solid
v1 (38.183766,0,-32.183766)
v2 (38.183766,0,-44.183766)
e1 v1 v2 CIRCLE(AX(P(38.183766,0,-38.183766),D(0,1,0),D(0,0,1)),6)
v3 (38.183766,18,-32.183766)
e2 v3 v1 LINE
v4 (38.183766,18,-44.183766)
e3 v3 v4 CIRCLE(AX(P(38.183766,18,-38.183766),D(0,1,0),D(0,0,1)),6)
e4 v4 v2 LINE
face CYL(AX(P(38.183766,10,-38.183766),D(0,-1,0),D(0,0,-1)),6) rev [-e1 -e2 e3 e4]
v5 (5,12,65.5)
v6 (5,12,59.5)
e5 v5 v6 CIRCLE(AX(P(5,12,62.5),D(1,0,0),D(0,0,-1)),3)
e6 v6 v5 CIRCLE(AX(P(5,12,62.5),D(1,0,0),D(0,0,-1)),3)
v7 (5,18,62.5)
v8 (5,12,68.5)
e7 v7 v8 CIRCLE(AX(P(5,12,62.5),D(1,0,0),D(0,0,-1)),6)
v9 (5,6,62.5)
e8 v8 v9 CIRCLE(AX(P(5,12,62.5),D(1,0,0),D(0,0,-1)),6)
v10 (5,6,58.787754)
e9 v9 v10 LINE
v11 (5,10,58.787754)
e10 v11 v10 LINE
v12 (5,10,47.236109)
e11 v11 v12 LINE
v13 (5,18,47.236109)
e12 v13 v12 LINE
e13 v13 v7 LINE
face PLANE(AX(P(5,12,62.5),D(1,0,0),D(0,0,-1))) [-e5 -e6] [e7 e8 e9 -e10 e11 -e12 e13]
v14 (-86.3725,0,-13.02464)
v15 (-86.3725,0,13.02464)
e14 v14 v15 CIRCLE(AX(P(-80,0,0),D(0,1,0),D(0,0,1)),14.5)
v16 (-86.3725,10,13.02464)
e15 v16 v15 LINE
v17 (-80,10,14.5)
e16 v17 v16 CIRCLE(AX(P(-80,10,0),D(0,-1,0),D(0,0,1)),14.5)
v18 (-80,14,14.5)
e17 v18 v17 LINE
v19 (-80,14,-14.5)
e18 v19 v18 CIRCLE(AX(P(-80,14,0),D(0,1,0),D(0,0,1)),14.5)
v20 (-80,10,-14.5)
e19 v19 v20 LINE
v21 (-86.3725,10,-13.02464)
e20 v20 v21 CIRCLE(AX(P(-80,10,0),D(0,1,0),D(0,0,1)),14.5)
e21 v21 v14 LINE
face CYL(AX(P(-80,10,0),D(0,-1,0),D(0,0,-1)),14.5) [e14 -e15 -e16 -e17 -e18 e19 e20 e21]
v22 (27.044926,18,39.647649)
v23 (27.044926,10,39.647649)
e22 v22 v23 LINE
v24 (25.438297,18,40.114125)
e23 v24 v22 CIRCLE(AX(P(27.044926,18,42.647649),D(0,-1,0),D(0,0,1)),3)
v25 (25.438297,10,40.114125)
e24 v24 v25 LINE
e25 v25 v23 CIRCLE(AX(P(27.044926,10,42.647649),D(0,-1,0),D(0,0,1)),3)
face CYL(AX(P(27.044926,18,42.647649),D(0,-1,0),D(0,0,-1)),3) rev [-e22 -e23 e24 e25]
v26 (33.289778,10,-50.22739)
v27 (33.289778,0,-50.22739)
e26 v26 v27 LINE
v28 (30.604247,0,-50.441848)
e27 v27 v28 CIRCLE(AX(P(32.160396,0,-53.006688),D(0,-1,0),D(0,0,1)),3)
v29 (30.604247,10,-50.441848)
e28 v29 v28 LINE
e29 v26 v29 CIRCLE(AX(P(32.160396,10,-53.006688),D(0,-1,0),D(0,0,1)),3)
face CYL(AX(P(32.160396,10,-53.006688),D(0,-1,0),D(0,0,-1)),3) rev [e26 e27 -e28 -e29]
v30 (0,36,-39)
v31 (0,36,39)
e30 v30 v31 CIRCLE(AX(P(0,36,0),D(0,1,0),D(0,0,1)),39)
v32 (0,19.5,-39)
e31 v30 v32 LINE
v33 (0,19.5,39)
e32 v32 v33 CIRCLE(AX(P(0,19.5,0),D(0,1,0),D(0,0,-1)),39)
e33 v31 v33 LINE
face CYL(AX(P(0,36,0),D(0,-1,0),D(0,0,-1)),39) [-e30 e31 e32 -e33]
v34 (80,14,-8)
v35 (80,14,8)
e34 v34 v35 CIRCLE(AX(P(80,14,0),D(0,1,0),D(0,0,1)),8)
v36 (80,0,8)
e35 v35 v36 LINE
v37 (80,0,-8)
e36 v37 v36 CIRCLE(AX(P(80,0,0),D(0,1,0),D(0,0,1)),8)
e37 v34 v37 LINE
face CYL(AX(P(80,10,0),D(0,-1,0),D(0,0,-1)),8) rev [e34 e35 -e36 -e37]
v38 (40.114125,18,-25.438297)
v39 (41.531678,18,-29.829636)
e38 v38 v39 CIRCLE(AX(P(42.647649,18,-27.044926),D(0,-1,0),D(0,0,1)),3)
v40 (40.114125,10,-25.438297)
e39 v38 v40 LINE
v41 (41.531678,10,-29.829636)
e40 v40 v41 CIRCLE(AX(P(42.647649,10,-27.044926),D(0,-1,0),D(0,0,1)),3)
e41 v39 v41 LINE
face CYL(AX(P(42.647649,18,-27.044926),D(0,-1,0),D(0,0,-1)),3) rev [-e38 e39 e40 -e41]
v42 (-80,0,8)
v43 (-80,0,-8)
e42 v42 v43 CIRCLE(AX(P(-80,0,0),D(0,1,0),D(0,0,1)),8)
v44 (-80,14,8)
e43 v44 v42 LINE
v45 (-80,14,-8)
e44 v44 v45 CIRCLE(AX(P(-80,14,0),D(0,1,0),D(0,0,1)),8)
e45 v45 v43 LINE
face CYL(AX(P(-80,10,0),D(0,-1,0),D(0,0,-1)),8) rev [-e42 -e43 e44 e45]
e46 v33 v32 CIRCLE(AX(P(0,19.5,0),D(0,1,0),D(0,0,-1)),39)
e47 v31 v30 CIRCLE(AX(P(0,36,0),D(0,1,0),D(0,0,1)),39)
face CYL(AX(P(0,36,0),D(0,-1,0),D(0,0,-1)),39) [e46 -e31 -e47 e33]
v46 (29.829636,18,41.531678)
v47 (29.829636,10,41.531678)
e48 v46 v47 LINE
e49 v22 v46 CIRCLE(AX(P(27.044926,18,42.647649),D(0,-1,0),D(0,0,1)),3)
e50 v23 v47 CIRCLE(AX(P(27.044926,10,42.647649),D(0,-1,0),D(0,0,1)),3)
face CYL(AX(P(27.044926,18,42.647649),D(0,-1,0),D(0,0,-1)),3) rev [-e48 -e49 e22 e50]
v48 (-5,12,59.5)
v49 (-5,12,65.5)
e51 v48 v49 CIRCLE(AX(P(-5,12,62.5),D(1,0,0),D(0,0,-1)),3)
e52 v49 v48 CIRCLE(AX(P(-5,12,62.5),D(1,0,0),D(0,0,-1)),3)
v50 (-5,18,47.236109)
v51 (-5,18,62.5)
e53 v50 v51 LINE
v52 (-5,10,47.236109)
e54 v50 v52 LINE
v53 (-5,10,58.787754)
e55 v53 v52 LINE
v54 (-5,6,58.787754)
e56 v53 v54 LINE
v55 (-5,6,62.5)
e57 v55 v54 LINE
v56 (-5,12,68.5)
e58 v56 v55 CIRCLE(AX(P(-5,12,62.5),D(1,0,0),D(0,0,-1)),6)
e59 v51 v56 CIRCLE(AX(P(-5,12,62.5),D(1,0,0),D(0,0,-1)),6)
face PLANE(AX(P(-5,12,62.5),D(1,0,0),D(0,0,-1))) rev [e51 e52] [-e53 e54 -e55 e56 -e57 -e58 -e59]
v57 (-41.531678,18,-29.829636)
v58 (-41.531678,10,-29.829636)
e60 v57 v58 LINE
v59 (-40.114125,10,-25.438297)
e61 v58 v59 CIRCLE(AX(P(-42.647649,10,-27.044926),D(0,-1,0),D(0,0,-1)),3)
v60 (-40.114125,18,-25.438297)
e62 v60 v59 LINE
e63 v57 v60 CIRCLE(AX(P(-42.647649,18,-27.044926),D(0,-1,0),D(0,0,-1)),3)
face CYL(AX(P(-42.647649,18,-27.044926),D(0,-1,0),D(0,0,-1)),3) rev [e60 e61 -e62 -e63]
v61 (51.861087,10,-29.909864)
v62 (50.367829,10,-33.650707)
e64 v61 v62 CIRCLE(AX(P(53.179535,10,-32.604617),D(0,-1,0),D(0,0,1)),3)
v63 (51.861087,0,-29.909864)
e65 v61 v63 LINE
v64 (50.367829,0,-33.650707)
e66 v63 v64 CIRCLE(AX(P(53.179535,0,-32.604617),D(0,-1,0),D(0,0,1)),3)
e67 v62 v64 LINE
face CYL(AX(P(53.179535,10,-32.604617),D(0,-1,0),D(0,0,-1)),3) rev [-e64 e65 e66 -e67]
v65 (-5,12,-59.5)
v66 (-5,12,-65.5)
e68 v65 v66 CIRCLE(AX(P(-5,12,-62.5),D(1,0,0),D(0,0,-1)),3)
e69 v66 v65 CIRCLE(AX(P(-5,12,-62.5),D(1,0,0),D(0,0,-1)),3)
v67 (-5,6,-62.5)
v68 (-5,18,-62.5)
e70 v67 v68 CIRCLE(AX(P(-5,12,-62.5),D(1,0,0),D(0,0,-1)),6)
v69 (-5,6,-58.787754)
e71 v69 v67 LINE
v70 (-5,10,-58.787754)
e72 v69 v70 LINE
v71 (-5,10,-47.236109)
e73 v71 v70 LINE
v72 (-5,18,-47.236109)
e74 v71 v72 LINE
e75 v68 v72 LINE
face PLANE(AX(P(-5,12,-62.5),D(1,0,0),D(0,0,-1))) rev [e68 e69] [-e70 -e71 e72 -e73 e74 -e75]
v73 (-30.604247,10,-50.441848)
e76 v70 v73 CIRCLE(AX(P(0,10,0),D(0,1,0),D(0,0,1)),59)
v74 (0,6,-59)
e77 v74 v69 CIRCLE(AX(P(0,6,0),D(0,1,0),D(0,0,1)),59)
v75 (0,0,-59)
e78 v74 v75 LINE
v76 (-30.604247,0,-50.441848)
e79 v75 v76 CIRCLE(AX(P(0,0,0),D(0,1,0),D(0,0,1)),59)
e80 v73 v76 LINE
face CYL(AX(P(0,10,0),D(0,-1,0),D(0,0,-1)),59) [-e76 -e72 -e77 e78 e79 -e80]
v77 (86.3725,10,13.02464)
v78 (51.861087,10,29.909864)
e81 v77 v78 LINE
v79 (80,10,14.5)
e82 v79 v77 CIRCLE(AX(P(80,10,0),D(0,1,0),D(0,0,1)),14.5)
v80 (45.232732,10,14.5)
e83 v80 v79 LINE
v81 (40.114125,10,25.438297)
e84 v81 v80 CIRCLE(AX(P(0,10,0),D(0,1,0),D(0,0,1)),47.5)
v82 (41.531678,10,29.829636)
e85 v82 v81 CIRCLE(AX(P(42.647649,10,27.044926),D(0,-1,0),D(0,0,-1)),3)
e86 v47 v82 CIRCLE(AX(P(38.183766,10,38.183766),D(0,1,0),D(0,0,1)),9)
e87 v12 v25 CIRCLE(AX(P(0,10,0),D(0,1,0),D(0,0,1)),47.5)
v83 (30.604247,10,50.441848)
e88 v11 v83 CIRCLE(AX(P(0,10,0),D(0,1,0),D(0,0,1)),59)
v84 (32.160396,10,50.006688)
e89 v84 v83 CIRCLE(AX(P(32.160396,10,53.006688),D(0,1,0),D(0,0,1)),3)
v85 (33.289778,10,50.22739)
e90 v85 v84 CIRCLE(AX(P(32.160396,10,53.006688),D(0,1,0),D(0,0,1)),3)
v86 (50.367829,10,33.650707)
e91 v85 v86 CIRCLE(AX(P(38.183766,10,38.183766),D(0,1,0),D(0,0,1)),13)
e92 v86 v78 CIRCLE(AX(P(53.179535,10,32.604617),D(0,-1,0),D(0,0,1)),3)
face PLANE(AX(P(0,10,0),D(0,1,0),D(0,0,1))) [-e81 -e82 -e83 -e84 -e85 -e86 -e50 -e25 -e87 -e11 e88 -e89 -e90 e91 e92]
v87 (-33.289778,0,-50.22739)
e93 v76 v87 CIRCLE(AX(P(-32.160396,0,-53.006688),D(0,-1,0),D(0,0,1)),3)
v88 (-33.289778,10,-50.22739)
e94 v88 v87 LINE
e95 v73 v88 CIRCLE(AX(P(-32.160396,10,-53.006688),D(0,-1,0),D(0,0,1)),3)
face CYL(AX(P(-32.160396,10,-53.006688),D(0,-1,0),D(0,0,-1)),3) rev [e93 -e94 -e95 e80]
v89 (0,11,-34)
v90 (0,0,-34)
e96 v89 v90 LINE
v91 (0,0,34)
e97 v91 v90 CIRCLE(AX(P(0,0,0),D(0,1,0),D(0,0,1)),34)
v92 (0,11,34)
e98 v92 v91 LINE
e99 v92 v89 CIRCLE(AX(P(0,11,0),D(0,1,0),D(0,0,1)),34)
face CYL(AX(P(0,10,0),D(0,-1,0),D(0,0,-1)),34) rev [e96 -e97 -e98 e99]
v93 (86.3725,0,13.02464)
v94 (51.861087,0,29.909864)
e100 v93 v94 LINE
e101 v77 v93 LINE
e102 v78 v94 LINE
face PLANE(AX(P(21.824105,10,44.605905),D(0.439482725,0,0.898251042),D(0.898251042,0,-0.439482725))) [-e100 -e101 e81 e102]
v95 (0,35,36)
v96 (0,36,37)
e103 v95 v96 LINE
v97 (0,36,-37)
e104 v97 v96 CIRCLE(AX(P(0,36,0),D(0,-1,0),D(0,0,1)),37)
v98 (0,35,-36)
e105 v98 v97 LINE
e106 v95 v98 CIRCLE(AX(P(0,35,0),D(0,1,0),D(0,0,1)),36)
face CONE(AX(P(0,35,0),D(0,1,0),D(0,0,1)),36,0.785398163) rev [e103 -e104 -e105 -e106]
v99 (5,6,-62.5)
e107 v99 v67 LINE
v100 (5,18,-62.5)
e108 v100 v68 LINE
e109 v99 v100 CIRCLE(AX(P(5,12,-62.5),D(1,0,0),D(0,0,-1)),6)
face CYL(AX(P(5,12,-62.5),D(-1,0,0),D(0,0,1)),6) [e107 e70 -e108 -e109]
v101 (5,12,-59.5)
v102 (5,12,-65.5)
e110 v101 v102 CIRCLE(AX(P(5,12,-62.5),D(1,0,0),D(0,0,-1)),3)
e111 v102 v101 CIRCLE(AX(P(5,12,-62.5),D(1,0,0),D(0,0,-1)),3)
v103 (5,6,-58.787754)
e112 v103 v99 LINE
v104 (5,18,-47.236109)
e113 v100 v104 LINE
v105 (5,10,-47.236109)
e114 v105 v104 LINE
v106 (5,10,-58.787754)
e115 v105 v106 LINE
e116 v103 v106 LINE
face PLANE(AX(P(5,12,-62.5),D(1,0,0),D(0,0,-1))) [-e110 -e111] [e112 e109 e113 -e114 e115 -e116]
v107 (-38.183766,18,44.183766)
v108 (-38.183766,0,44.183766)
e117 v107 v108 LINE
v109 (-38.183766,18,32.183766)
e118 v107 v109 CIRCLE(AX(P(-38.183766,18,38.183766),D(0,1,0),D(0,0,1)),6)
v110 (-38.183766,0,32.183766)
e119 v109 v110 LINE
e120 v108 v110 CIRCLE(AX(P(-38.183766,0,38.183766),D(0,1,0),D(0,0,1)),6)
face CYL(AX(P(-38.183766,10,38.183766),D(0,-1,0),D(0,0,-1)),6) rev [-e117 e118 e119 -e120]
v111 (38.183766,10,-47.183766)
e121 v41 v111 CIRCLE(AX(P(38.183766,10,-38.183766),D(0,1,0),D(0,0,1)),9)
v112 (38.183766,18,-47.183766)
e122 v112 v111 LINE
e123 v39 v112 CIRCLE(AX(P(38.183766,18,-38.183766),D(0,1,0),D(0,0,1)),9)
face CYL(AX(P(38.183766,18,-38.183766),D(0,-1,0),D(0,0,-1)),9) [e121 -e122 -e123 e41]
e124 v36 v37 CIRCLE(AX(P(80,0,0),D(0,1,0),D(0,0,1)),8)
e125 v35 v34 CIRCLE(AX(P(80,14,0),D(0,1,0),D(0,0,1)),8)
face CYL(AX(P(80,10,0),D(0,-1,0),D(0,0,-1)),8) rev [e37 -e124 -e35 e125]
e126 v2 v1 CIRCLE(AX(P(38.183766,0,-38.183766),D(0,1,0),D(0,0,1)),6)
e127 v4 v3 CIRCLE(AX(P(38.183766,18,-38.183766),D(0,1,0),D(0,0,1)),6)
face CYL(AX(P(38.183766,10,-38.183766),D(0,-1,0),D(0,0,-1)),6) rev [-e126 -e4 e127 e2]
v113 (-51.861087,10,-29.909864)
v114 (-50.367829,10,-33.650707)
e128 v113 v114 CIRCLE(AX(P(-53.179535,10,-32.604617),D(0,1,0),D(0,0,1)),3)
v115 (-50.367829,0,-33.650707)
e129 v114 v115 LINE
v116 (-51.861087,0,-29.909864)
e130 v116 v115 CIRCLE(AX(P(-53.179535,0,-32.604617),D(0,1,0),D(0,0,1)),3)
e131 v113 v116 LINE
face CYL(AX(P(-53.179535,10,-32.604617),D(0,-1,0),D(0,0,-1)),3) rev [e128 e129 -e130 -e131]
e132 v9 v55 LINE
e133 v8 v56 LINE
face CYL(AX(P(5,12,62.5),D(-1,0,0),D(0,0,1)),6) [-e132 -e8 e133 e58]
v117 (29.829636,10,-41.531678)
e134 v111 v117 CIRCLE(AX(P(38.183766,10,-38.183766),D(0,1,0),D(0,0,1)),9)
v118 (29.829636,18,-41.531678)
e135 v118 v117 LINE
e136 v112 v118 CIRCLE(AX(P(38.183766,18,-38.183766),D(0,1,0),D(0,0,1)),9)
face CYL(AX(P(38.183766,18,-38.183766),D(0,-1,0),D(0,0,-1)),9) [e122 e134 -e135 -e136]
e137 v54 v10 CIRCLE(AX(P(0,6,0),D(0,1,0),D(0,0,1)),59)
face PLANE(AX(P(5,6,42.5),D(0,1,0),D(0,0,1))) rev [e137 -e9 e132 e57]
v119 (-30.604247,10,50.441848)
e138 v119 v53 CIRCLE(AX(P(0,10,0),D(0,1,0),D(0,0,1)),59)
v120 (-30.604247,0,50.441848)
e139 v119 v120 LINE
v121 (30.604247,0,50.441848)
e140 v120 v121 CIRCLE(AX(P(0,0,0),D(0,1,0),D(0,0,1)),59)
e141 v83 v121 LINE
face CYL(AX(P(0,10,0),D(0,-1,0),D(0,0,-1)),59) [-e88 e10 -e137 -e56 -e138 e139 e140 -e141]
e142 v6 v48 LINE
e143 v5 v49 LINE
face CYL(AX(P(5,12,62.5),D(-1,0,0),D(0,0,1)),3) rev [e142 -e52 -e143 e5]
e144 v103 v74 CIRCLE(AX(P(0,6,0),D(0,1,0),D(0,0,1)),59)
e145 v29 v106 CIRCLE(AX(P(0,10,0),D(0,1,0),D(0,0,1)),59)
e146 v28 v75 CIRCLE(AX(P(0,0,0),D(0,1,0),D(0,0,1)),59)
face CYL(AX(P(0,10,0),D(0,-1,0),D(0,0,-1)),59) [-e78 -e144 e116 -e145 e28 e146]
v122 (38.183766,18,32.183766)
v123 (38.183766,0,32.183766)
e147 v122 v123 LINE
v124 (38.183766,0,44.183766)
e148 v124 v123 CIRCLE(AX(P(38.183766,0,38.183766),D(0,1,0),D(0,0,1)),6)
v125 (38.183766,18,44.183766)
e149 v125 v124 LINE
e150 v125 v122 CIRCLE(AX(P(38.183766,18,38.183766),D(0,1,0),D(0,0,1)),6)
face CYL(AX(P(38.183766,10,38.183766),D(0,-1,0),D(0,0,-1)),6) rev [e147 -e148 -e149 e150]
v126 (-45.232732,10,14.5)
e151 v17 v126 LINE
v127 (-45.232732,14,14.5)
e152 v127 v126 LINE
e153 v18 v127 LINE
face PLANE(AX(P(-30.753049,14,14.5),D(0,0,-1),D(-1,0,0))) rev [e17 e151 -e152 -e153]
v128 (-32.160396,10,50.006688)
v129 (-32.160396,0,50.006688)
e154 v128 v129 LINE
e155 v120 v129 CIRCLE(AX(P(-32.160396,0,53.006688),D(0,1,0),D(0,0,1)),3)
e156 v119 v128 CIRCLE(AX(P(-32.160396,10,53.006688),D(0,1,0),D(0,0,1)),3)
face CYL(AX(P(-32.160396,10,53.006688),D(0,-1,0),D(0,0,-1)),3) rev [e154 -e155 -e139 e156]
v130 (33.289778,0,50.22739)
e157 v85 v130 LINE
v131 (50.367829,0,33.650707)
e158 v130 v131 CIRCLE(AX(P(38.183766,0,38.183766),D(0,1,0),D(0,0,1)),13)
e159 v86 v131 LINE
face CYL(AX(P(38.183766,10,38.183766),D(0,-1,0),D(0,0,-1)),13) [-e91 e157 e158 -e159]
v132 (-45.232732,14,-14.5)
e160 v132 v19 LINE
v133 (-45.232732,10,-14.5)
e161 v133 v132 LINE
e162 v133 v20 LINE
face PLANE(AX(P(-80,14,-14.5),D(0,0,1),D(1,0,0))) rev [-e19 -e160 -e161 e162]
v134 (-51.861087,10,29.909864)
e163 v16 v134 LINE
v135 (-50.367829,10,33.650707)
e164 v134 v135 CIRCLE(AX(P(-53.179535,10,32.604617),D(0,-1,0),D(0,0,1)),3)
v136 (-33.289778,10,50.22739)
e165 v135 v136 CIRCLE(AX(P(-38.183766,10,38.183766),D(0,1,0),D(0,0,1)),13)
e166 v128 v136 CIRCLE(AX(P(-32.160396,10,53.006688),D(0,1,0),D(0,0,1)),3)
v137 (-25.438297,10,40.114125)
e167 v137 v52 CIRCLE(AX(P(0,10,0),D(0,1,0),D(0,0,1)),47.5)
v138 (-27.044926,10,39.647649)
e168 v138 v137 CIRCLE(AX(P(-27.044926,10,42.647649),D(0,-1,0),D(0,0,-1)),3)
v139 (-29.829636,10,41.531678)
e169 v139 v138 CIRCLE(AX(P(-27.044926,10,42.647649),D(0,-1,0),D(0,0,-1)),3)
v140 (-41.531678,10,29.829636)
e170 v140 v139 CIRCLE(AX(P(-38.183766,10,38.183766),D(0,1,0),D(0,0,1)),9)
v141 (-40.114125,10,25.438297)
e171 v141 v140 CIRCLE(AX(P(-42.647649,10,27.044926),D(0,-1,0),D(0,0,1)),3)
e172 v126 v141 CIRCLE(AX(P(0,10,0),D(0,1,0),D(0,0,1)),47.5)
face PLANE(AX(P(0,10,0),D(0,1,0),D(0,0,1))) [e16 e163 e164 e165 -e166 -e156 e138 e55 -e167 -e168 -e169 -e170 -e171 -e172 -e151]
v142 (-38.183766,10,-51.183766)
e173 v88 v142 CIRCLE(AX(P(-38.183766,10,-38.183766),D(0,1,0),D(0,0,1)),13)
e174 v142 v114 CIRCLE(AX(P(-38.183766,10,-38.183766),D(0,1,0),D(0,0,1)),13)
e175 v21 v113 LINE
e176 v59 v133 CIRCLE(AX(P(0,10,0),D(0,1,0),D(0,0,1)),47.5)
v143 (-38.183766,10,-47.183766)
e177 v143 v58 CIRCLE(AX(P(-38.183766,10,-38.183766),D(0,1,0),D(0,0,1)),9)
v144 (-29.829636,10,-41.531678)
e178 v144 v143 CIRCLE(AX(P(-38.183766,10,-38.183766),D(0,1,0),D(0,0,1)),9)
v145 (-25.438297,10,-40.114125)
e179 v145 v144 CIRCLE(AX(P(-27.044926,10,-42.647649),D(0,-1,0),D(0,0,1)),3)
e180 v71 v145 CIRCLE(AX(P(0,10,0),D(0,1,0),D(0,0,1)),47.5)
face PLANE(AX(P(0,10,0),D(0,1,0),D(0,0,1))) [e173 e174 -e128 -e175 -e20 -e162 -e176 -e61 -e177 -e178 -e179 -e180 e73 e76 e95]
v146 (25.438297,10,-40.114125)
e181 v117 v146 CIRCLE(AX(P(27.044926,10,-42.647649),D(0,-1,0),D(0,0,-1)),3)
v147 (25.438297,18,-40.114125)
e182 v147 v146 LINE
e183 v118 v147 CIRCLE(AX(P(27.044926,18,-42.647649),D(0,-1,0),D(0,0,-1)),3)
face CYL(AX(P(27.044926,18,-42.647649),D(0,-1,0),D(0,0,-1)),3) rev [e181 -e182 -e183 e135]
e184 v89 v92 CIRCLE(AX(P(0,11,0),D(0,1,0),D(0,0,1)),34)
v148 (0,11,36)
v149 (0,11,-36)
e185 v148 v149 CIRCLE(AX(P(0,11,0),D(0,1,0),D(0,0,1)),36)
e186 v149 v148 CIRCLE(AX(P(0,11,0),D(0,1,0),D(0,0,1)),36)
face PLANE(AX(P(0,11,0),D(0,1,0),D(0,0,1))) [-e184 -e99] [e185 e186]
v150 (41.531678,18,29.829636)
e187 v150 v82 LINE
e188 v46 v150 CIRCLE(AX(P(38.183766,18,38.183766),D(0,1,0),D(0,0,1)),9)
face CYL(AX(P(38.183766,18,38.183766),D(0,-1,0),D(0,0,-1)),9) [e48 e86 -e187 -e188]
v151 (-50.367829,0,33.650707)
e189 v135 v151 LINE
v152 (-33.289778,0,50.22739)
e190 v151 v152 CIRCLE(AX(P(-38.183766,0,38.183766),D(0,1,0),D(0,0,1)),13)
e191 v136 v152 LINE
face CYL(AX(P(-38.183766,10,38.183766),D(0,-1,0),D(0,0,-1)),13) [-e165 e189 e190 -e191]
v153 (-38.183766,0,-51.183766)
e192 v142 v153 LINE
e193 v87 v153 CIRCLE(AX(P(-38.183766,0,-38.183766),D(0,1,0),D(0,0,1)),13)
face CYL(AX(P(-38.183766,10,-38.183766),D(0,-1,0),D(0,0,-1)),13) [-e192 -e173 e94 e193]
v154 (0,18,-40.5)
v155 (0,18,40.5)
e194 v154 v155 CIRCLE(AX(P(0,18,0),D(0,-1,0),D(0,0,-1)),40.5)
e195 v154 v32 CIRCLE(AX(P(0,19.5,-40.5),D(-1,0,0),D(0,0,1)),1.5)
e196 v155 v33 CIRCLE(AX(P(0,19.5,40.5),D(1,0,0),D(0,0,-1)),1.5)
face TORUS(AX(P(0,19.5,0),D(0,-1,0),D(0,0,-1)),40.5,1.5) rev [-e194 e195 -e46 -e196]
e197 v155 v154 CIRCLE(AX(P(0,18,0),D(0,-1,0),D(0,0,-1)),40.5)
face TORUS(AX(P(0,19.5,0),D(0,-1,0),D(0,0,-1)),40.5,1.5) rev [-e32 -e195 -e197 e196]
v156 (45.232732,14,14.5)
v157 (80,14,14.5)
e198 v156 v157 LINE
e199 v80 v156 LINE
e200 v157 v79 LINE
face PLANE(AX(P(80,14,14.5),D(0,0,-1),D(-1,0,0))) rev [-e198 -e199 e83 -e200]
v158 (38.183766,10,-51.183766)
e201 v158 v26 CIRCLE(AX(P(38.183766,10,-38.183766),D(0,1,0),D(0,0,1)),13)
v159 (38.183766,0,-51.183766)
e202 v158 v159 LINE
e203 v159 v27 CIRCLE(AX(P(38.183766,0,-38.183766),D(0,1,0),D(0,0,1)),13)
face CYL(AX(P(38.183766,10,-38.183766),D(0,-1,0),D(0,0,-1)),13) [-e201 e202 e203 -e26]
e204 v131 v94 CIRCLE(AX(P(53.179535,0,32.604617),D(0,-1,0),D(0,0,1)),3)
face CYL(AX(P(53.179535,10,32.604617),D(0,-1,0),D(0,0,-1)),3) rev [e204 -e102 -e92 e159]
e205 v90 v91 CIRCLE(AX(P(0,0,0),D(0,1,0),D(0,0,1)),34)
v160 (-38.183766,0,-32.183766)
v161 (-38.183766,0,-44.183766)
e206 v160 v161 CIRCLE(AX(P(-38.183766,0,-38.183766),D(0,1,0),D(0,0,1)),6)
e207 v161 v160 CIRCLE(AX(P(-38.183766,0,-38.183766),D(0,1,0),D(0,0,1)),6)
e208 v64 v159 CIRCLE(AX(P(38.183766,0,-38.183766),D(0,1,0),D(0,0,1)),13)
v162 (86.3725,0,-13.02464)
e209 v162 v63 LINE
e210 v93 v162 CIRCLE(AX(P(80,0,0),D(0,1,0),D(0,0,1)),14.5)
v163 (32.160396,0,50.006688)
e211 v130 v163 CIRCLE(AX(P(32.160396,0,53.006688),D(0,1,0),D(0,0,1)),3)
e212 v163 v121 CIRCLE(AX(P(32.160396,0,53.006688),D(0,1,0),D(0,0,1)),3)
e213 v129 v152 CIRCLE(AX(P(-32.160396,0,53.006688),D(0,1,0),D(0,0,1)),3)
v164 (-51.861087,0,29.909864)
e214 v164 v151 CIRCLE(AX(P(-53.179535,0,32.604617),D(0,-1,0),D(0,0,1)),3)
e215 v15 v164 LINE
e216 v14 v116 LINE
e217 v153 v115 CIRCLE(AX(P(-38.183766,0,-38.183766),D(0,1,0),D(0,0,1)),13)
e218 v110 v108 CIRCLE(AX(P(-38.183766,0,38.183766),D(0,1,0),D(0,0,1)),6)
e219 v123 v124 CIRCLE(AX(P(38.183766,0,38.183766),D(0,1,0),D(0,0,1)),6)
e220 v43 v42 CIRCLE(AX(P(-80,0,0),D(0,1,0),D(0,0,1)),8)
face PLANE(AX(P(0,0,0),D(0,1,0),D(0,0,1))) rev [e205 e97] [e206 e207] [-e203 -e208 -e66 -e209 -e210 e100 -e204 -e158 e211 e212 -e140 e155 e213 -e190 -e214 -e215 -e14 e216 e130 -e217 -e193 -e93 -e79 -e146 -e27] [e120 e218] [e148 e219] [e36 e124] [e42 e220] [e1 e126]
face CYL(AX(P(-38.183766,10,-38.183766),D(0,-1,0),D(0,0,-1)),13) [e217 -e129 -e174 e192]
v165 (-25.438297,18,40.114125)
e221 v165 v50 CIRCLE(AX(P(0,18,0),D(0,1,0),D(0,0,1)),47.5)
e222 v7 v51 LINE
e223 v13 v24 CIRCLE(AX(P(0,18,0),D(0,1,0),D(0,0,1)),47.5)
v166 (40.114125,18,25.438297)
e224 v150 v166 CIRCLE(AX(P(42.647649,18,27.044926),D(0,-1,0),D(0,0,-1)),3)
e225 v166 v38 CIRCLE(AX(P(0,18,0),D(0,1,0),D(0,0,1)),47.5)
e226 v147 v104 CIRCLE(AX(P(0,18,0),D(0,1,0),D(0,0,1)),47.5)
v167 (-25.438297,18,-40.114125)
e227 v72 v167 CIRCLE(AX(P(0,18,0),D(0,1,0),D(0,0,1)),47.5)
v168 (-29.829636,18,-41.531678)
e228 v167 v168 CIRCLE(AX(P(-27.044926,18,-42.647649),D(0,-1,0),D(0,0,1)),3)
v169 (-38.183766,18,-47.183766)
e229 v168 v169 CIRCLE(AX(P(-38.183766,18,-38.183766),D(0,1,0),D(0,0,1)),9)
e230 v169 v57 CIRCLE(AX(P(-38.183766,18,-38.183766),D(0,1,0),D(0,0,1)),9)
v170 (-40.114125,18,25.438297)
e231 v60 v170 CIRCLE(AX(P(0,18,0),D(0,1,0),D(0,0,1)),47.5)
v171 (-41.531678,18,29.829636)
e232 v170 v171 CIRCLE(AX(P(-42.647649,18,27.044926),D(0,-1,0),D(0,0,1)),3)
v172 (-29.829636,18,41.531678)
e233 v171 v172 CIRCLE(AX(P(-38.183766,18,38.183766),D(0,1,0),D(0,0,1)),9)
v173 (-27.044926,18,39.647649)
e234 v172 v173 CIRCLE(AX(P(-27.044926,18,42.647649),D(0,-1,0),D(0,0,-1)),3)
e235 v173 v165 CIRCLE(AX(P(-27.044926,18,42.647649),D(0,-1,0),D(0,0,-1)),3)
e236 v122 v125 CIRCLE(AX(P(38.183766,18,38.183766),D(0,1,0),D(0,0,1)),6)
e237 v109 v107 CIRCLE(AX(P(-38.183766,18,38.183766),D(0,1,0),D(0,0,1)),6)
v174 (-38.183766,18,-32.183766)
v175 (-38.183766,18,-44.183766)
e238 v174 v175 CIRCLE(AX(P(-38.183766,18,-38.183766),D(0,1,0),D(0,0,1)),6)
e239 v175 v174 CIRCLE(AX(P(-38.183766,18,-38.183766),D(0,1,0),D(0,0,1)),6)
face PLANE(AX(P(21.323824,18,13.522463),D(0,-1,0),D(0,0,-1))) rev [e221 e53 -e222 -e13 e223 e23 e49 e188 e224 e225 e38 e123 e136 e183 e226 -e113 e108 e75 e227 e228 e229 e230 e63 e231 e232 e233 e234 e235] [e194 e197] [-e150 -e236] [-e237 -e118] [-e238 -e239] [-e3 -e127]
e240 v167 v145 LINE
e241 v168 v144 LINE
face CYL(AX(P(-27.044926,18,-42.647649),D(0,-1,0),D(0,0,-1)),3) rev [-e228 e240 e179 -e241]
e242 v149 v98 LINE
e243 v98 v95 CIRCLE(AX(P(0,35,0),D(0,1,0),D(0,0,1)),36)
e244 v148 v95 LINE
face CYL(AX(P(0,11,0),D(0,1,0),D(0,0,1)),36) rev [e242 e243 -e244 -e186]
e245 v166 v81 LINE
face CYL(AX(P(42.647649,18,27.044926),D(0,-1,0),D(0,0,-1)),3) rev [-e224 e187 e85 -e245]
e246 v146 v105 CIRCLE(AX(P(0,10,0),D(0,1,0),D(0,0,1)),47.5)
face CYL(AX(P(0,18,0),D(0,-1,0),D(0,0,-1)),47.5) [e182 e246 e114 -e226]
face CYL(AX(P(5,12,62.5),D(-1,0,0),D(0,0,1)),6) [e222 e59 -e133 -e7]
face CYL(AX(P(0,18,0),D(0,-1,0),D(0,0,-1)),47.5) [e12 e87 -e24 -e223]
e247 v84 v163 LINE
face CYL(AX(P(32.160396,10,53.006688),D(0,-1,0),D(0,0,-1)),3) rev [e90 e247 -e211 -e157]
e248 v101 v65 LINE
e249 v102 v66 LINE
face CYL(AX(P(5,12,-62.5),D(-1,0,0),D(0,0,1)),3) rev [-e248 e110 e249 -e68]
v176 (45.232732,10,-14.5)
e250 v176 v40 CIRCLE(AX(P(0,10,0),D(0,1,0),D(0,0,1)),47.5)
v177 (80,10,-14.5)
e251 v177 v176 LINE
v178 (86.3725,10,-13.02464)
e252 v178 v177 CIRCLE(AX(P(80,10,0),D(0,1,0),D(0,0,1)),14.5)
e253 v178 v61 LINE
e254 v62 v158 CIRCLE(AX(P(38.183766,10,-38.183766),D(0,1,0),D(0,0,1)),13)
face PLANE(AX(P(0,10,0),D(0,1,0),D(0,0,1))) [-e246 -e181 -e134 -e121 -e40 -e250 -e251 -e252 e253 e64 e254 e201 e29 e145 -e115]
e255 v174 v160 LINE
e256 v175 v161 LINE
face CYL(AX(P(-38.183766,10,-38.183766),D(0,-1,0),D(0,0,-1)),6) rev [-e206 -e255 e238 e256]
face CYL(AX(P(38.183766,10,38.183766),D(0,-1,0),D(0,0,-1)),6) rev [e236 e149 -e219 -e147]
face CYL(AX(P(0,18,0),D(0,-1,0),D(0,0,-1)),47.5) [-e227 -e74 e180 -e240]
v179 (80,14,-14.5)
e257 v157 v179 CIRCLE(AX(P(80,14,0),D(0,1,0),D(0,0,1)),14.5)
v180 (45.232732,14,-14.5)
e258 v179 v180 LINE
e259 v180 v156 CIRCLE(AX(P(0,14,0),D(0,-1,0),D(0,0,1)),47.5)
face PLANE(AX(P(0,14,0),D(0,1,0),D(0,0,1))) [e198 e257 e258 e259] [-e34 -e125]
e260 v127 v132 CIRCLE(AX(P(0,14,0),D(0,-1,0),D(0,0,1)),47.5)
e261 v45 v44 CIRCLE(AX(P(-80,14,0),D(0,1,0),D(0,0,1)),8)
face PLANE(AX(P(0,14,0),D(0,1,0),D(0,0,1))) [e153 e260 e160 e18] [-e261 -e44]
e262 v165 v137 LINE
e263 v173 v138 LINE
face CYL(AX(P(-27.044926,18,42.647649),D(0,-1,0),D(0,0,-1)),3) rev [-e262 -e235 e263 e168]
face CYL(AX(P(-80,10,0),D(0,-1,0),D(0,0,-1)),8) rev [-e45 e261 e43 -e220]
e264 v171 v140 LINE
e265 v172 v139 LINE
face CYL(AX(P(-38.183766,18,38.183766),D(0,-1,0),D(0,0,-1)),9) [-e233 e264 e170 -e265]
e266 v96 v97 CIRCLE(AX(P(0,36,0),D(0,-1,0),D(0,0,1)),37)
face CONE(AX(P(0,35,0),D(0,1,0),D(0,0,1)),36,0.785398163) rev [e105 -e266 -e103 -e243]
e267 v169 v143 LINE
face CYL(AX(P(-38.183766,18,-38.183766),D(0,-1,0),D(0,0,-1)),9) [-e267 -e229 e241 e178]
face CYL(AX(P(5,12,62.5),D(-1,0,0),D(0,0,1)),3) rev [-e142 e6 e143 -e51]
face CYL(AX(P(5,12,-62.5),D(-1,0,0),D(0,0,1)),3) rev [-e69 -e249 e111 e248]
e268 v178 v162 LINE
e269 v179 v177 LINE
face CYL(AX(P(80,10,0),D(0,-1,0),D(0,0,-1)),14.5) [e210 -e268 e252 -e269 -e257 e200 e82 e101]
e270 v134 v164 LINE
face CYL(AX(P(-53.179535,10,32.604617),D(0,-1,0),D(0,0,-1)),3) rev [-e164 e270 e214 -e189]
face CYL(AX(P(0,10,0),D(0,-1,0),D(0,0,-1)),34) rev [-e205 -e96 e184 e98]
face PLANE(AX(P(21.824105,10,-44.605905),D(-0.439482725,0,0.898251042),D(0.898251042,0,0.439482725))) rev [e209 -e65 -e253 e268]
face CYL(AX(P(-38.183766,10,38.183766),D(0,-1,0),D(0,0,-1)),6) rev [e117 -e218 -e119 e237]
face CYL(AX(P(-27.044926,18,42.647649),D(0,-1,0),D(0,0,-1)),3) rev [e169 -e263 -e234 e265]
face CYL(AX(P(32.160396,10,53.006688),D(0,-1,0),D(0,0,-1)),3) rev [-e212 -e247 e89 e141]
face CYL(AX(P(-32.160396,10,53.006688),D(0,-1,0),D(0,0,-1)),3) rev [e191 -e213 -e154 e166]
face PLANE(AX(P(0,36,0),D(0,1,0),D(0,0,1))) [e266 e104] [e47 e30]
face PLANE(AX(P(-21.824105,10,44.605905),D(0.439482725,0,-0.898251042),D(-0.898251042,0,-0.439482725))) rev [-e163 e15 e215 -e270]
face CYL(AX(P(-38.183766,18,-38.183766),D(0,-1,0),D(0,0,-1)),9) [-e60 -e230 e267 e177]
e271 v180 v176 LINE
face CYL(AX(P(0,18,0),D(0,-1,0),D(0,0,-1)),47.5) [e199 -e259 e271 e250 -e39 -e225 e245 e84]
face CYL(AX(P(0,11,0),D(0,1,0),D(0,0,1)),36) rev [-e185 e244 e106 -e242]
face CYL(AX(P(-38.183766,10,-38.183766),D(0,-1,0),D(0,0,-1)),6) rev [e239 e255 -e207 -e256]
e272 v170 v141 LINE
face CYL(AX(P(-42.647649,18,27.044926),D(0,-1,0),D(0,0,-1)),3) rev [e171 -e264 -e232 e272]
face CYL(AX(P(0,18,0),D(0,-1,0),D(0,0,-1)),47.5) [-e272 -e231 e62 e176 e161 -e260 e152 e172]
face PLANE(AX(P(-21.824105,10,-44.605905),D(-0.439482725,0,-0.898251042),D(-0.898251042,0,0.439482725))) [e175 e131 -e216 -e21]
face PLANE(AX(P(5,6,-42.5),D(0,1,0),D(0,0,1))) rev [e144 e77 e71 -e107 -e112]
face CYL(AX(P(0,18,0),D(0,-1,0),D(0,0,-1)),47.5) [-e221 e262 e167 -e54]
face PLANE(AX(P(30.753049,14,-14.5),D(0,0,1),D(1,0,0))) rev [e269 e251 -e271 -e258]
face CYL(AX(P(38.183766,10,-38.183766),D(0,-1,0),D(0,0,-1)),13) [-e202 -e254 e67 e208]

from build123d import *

# Parameters (mm, degrees)
BASE_FLANGE_SKETCH_R      = 8
BASE_FLANGE_SKETCH_R_2    = 34
BASE_FLANGE_SKETCH_R_3    = 6
BASE_FLANGE_DEPTH         = 10
RAISED_PAD_SKETCH_R       = 8
RAISED_PAD_DEPTH          = 4
BOLT_BOSS_RING_SKETCH_R   = 6
BOLT_BOSS_RING_SKETCH_R_2 = 34
BOLT_BOSS_RING_DEPTH      = 8
BEARING_SPIGOT_SKETCH_R   = 39
BEARING_SPIGOT_SKETCH_R_2 = 34
BEARING_SPIGOT_78_DEPTH   = 18
SPIGOT_ROOT_FILLET_R1_5_R = 1.5
BEARING_BORE_SKETCH_R     = 36
BEARING_BORE_72_DEPTH     = 25
BORE_CHAMFER_1X45_SIZE    = 1
SIDE_LUGS_SKETCH_R        = 3
SIDE_LUGS_DEPTH           = 5


with BuildPart() as part:
    # Base Flange Sketch → Base Flange (new body)
    # profile 1 of 5: a face of its own
    with BuildSketch(Plane(origin=(0, 0, 0), x_dir=(1, 0, 0), z_dir=(0, 1, 0))):
        with BuildLine():
            ThreePointArc((-80, 14.5), (-83.270528886, 14.126345628), (-86.372499507, 13.024640112))
            ThreePointArc((-86.372499507, 13.024640112), (-94.5, 0), (-86.372499507, -13.024640112))
            ThreePointArc((-86.372499507, -13.024640112), (-83.270528886, -14.126345628), (-80, -14.5))
            Line((-80, -14.5), (-45.232731512, -14.5))
            ThreePointArc((-45.232731512, -14.5), (-47.5, 0), (-45.232731512, 14.5))
            Line((-45.232731512, 14.5), (-80, 14.5))
        make_face()
        with Locations(Location((-80, 0, 0), (0, 0, 270))):
            Circle(BASE_FLANGE_SKETCH_R, mode=Mode.SUBTRACT)
    # profile 2 of 5: a face of its own
    with BuildSketch(Plane(origin=(0, 0, 0), x_dir=(1, 0, 0), z_dir=(0, 1, 0))):
        with BuildLine():
            ThreePointArc((-80, -14.5), (-83.270528886, -14.126345628), (-86.372499507, -13.024640112))
            Line((-86.372499507, -13.024640112), (-51.861087106, -29.909863551))
            ThreePointArc((-51.861087106, -29.909863551), (-50.393315143, -31.492421844), (-50.367828575, -33.65070721))
            ThreePointArc((-50.367828575, -33.65070721), (-47.238206932, -47.512061995), (-33.289777567, -50.227390033))
            ThreePointArc((-33.289777567, -50.227390033), (-31.921585171, -50.016208018), (-30.604247405, -50.44184811))
            ThreePointArc((-30.604247405, -50.44184811), (0, -59), (30.604247405, -50.44184811))
            ThreePointArc((30.604247405, -50.44184811), (31.921585171, -50.016208018), (33.289777567, -50.227390033))
            ThreePointArc((33.289777567, -50.227390033), (47.238206932, -47.512061995), (50.367828575, -33.65070721))
            ThreePointArc((50.367828575, -33.65070721), (50.393315143, -31.492421844), (51.861087106, -29.909863551))
            Line((51.861087106, -29.909863551), (86.372499507, -13.024640112))
            ThreePointArc((86.372499507, -13.024640112), (83.270528886, -14.126345628), (80, -14.5))
            Line((80, -14.5), (45.232731512, -14.5))
            ThreePointArc((45.232731512, -14.5), (43.022471721, -20.132484374), (40.114125183, -25.438297128))
            ThreePointArc((40.114125183, -25.438297128), (39.792711515, -27.966518872), (41.531678205, -29.829636361))
            ThreePointArc((41.531678205, -29.829636361), (44.547727215, -44.547727215), (29.829636361, -41.531678205))
            ThreePointArc((29.829636361, -41.531678205), (27.966518872, -39.792711515), (25.438297128, -40.114125183))
            ThreePointArc((25.438297128, -40.114125183), (0, -47.5), (-25.438297128, -40.114125183))
            ThreePointArc((-25.438297128, -40.114125183), (-27.966518872, -39.792711515), (-29.829636361, -41.531678205))
            ThreePointArc((-29.829636361, -41.531678205), (-44.547727215, -44.547727215), (-41.531678205, -29.829636361))
            ThreePointArc((-41.531678205, -29.829636361), (-39.792711515, -27.966518872), (-40.114125183, -25.438297128))
            ThreePointArc((-40.114125183, -25.438297128), (-43.022471721, -20.132484374), (-45.232731512, -14.5))
            Line((-45.232731512, -14.5), (-80, -14.5))
        make_face()
    # profile 3 of 5: a face of its own
    with BuildSketch(Plane(origin=(0, 0, 0), x_dir=(1, 0, 0), z_dir=(0, 1, 0))):
        with BuildLine():
            Line((-51.861087106, 29.909863551), (-86.372499507, 13.024640112))
            ThreePointArc((-86.372499507, 13.024640112), (-83.270528886, 14.126345628), (-80, 14.5))
            Line((-80, 14.5), (-45.232731512, 14.5))
            ThreePointArc((-45.232731512, 14.5), (-43.022471721, 20.132484374), (-40.114125183, 25.438297128))
            ThreePointArc((-40.114125183, 25.438297128), (-39.792711515, 27.966518872), (-41.531678205, 29.829636361))
            ThreePointArc((-41.531678205, 29.829636361), (-44.547727215, 44.547727215), (-29.829636361, 41.531678205))
            ThreePointArc((-29.829636361, 41.531678205), (-27.966518872, 39.792711515), (-25.438297128, 40.114125183))
            ThreePointArc((-25.438297128, 40.114125183), (0, 47.5), (25.438297128, 40.114125183))
            ThreePointArc((25.438297128, 40.114125183), (27.966518872, 39.792711515), (29.829636361, 41.531678205))
            ThreePointArc((29.829636361, 41.531678205), (44.547727215, 44.547727215), (41.531678205, 29.829636361))
            ThreePointArc((41.531678205, 29.829636361), (39.792711515, 27.966518872), (40.114125183, 25.438297128))
            ThreePointArc((40.114125183, 25.438297128), (43.022471721, 20.132484374), (45.232731512, 14.5))
            Line((45.232731512, 14.5), (80, 14.5))
            ThreePointArc((80, 14.5), (83.270528886, 14.126345628), (86.372499507, 13.024640112))
            Line((86.372499507, 13.024640112), (51.861087106, 29.909863551))
            ThreePointArc((51.861087106, 29.909863551), (50.393315143, 31.492421844), (50.367828575, 33.65070721))
            ThreePointArc((50.367828575, 33.65070721), (47.238206932, 47.512061995), (33.289777567, 50.227390033))
            ThreePointArc((33.289777567, 50.227390033), (31.921585171, 50.016208018), (30.604247405, 50.44184811))
            ThreePointArc((30.604247405, 50.44184811), (0, 59), (-30.604247405, 50.44184811))
            ThreePointArc((-30.604247405, 50.44184811), (-31.921585171, 50.016208018), (-33.289777567, 50.227390033))
            ThreePointArc((-33.289777567, 50.227390033), (-47.238206932, 47.512061995), (-50.367828575, 33.65070721))
            ThreePointArc((-50.367828575, 33.65070721), (-50.393315143, 31.492421844), (-51.861087106, 29.909863551))
        make_face()
    # profile 4 of 5: a face of its own
    with BuildSketch(Plane(origin=(0, 0, 0), x_dir=(1, 0, 0), z_dir=(0, 1, 0))):
        with BuildLine():
            ThreePointArc((86.372499507, -13.024640112), (94.5, 0), (86.372499507, 13.024640112))
            ThreePointArc((86.372499507, 13.024640112), (83.270528886, 14.126345628), (80, 14.5))
            Line((80, 14.5), (45.232731512, 14.5))
            ThreePointArc((45.232731512, 14.5), (47.5, 0), (45.232731512, -14.5))
            Line((45.232731512, -14.5), (80, -14.5))
            ThreePointArc((80, -14.5), (83.270528886, -14.126345628), (86.372499507, -13.024640112))
        make_face()
        with Locations(Location((80, 0, 0), (0, 0, 270))):
            Circle(BASE_FLANGE_SKETCH_R, mode=Mode.SUBTRACT)
    # profile 5 of 5: a face of its own
    with BuildSketch(Plane(origin=(0, 0, 0), x_dir=(1, 0, 0), z_dir=(0, 1, 0))):
        with BuildLine():
            ThreePointArc((-41.531678205, -29.829636361), (-44.547727215, -44.547727215), (-29.829636361, -41.531678205))
            ThreePointArc((-29.829636361, -41.531678205), (-27.966518872, -39.792711515), (-25.438297128, -40.114125183))
            ThreePointArc((-25.438297128, -40.114125183), (0, -47.5), (25.438297128, -40.114125183))
            ThreePointArc((25.438297128, -40.114125183), (27.966518872, -39.792711515), (29.829636361, -41.531678205))
            ThreePointArc((29.829636361, -41.531678205), (44.547727215, -44.547727215), (41.531678205, -29.829636361))
            ThreePointArc((41.531678205, -29.829636361), (39.792711515, -27.966518872), (40.114125183, -25.438297128))
            ThreePointArc((40.114125183, -25.438297128), (47.5, 0), (40.114125183, 25.438297128))
            ThreePointArc((40.114125183, 25.438297128), (39.792711515, 27.966518872), (41.531678205, 29.829636361))
            ThreePointArc((41.531678205, 29.829636361), (44.547727215, 44.547727215), (29.829636361, 41.531678205))
            ThreePointArc((29.829636361, 41.531678205), (27.966518872, 39.792711515), (25.438297128, 40.114125183))
            ThreePointArc((25.438297128, 40.114125183), (0, 47.5), (-25.438297128, 40.114125183))
            ThreePointArc((-25.438297128, 40.114125183), (-27.966518872, 39.792711515), (-29.829636361, 41.531678205))
            ThreePointArc((-29.829636361, 41.531678205), (-44.547727215, 44.547727215), (-41.531678205, 29.829636361))
            ThreePointArc((-41.531678205, 29.829636361), (-39.792711515, 27.966518872), (-40.114125183, 25.438297128))
            ThreePointArc((-40.114125183, 25.438297128), (-47.5, 0), (-40.114125183, -25.438297128))
            ThreePointArc((-40.114125183, -25.438297128), (-39.792711515, -27.966518872), (-41.531678205, -29.829636361))
        make_face()
        with Locations(Location((0, 0, 0), (0, 0, 270))):
            Circle(BASE_FLANGE_SKETCH_R_2, mode=Mode.SUBTRACT)
        with Locations(Location((-38.183766184, 38.183766184, 0), (0, 0, 270))):
            Circle(BASE_FLANGE_SKETCH_R_3, mode=Mode.SUBTRACT)
        with Locations(Location((38.183766184, 38.183766184, 0), (0, 0, 270))):
            Circle(BASE_FLANGE_SKETCH_R_3, mode=Mode.SUBTRACT)
        with Locations(Location((38.183766184, -38.183766184, 0), (0, 0, 270))):
            Circle(BASE_FLANGE_SKETCH_R_3, mode=Mode.SUBTRACT)
        with Locations(Location((-38.183766184, -38.183766184, 0), (0, 0, 270))):
            Circle(BASE_FLANGE_SKETCH_R_3, mode=Mode.SUBTRACT)
    extrude(amount=BASE_FLANGE_DEPTH)

    # Raised Pad Sketch → Raised Pad (add)
    # profile 1 of 2: a face of its own
    with BuildSketch(Plane(origin=(0, 10, 0), x_dir=(1, 0, 0), z_dir=(0, 1, 0))):
        with BuildLine():
            Line((-80, 14.5), (-30.753048629, 14.5))
            ThreePointArc((-30.753048629, 14.5), (-34, 0), (-30.753048629, -14.5))
            Line((-30.753048629, -14.5), (-80, -14.5))
            ThreePointArc((-80, -14.5), (-94.5, 0), (-80, 14.5))
        make_face()
        with Locations(Location((-80, 0, 0), (0, 0, 270))):
            Circle(RAISED_PAD_SKETCH_R, mode=Mode.SUBTRACT)
    # profile 2 of 2: a face of its own
    with BuildSketch(Plane(origin=(0, 10, 0), x_dir=(1, 0, 0), z_dir=(0, 1, 0))):
        with BuildLine():
            Line((80, -14.5), (30.753048629, -14.5))
            ThreePointArc((30.753048629, -14.5), (34, 0), (30.753048629, 14.5))
            Line((30.753048629, 14.5), (80, 14.5))
            ThreePointArc((80, 14.5), (94.5, 0), (80, -14.5))
        make_face()
        with Locations(Location((80, 0, 0), (0, 0, 270))):
            Circle(RAISED_PAD_SKETCH_R, mode=Mode.SUBTRACT)
    extrude(amount=RAISED_PAD_DEPTH)

    # Bolt Boss Ring Sketch → Bolt Boss Ring (add)
    with BuildSketch(Plane(origin=(0, 10, 0), x_dir=(1, 0, 0), z_dir=(0, 1, 0))):
        with BuildLine():
            ThreePointArc((-29.829636361, 41.531678205), (-44.547727215, 44.547727215), (-41.531678205, 29.829636361))
            ThreePointArc((-41.531678205, 29.829636361), (-39.792711515, 27.966518872), (-40.114125183, 25.438297128))
            ThreePointArc((-40.114125183, 25.438297128), (-47.5, 0), (-40.114125183, -25.438297128))
            ThreePointArc((-40.114125183, -25.438297128), (-39.792711515, -27.966518872), (-41.531678205, -29.829636361))
            ThreePointArc((-41.531678205, -29.829636361), (-44.547727215, -44.547727215), (-29.829636361, -41.531678205))
            ThreePointArc((-29.829636361, -41.531678205), (-27.966518872, -39.792711515), (-25.438297128, -40.114125183))
            ThreePointArc((-25.438297128, -40.114125183), (0, -47.5), (25.438297128, -40.114125183))
            ThreePointArc((25.438297128, -40.114125183), (27.966518872, -39.792711515), (29.829636361, -41.531678205))
            ThreePointArc((29.829636361, -41.531678205), (44.547727215, -44.547727215), (41.531678205, -29.829636361))
            ThreePointArc((41.531678205, -29.829636361), (39.792711515, -27.966518872), (40.114125183, -25.438297128))
            ThreePointArc((40.114125183, -25.438297128), (47.5, 0), (40.114125183, 25.438297128))
            ThreePointArc((40.114125183, 25.438297128), (39.792711515, 27.966518872), (41.531678205, 29.829636361))
            ThreePointArc((41.531678205, 29.829636361), (44.547727215, 44.547727215), (29.829636361, 41.531678205))
            ThreePointArc((29.829636361, 41.531678205), (27.966518872, 39.792711515), (25.438297128, 40.114125183))
            ThreePointArc((25.438297128, 40.114125183), (0, 47.5), (-25.438297128, 40.114125183))
            ThreePointArc((-25.438297128, 40.114125183), (-27.966518872, 39.792711515), (-29.829636361, 41.531678205))
        make_face()
        with Locations(Location((-38.183766184, 38.183766184, 0), (0, 0, 270))):
            Circle(BOLT_BOSS_RING_SKETCH_R, mode=Mode.SUBTRACT)
        with Locations(Location((38.183766184, 38.183766184, 0), (0, 0, 270))):
            Circle(BOLT_BOSS_RING_SKETCH_R, mode=Mode.SUBTRACT)
        with Locations(Location((38.183766184, -38.183766184, 0), (0, 0, 270))):
            Circle(BOLT_BOSS_RING_SKETCH_R, mode=Mode.SUBTRACT)
        with Locations(Location((-38.183766184, -38.183766184, 0), (0, 0, 270))):
            Circle(BOLT_BOSS_RING_SKETCH_R, mode=Mode.SUBTRACT)
        with Locations(Location((0, 0, 0), (0, 0, 270))):
            Circle(BOLT_BOSS_RING_SKETCH_R_2, mode=Mode.SUBTRACT)
    extrude(amount=BOLT_BOSS_RING_DEPTH)

    # Bearing Spigot Sketch → Bearing Spigot Ø78 (add)
    with BuildSketch(Plane(origin=(0, 18, 0), x_dir=(1, 0, 0), z_dir=(0, 1, 0))):
        with Locations(Location((0, 0, 0), (0, 0, 270))):
            Circle(BEARING_SPIGOT_SKETCH_R)
        with Locations(Location((0, 0, 0), (0, 0, 270))):
            Circle(BEARING_SPIGOT_SKETCH_R_2, mode=Mode.SUBTRACT)
    extrude(amount=BEARING_SPIGOT_78_DEPTH)

    # Spigot Root Fillet R1.5
    spigot_root_fillet_r1_5_edges = [part.edges().sort_by_distance(p)[0] for p in [
        (0, 18, -39),
    ]]
    fillet(spigot_root_fillet_r1_5_edges, radius=SPIGOT_ROOT_FILLET_R1_5_R)

    # Bearing Bore Sketch → Bearing Bore Ø72 (cut)
    with BuildSketch(Plane(origin=(0, 36, 0), x_dir=(1, 0, 0), z_dir=(0, 1, 0))):
        with Locations(Location((0, 0, 0), (0, 0, 270))):
            Circle(BEARING_BORE_SKETCH_R)
    extrude(amount=-BEARING_BORE_72_DEPTH, mode=Mode.SUBTRACT)

    # Bore Chamfer 1x45
    bore_chamfer_1x45_edges = [part.edges().sort_by_distance(p)[0] for p in [
        (0, 36, -36),
    ]]
    chamfer(bore_chamfer_1x45_edges, length=BORE_CHAMFER_1X45_SIZE)

    # Side Lugs Sketch → Side Lugs (add, symmetric)
    # profile 1 of 2: a face of its own
    with BuildSketch(Plane(origin=(0, 0, 0), x_dir=(0, 0, -1), z_dir=(1, 0, 0))):
        with BuildLine():
            Line((-62.5, 18), (-42.5, 18))
            Line((-42.5, 18), (-42.5, 6))
            Line((-42.5, 6), (-62.5, 6))
            ThreePointArc((-62.5, 6), (-68.5, 12), (-62.5, 18))
        make_face()
        with Locations((-62.5, 12)):
            Circle(SIDE_LUGS_SKETCH_R, mode=Mode.SUBTRACT)
    # profile 2 of 2: a face of its own
    with BuildSketch(Plane(origin=(0, 0, 0), x_dir=(0, 0, -1), z_dir=(1, 0, 0))):
        with BuildLine():
            Line((62.5, 18), (42.5, 18))
            Line((42.5, 18), (42.5, 6))
            Line((42.5, 6), (62.5, 6))
            ThreePointArc((62.5, 6), (68.5, 12), (62.5, 18))
        make_face()
        with Locations((62.5, 12)):
            Circle(SIDE_LUGS_SKETCH_R, mode=Mode.SUBTRACT)
    extrude(amount=SIDE_LUGS_DEPTH, both=True)


solid = part.part
